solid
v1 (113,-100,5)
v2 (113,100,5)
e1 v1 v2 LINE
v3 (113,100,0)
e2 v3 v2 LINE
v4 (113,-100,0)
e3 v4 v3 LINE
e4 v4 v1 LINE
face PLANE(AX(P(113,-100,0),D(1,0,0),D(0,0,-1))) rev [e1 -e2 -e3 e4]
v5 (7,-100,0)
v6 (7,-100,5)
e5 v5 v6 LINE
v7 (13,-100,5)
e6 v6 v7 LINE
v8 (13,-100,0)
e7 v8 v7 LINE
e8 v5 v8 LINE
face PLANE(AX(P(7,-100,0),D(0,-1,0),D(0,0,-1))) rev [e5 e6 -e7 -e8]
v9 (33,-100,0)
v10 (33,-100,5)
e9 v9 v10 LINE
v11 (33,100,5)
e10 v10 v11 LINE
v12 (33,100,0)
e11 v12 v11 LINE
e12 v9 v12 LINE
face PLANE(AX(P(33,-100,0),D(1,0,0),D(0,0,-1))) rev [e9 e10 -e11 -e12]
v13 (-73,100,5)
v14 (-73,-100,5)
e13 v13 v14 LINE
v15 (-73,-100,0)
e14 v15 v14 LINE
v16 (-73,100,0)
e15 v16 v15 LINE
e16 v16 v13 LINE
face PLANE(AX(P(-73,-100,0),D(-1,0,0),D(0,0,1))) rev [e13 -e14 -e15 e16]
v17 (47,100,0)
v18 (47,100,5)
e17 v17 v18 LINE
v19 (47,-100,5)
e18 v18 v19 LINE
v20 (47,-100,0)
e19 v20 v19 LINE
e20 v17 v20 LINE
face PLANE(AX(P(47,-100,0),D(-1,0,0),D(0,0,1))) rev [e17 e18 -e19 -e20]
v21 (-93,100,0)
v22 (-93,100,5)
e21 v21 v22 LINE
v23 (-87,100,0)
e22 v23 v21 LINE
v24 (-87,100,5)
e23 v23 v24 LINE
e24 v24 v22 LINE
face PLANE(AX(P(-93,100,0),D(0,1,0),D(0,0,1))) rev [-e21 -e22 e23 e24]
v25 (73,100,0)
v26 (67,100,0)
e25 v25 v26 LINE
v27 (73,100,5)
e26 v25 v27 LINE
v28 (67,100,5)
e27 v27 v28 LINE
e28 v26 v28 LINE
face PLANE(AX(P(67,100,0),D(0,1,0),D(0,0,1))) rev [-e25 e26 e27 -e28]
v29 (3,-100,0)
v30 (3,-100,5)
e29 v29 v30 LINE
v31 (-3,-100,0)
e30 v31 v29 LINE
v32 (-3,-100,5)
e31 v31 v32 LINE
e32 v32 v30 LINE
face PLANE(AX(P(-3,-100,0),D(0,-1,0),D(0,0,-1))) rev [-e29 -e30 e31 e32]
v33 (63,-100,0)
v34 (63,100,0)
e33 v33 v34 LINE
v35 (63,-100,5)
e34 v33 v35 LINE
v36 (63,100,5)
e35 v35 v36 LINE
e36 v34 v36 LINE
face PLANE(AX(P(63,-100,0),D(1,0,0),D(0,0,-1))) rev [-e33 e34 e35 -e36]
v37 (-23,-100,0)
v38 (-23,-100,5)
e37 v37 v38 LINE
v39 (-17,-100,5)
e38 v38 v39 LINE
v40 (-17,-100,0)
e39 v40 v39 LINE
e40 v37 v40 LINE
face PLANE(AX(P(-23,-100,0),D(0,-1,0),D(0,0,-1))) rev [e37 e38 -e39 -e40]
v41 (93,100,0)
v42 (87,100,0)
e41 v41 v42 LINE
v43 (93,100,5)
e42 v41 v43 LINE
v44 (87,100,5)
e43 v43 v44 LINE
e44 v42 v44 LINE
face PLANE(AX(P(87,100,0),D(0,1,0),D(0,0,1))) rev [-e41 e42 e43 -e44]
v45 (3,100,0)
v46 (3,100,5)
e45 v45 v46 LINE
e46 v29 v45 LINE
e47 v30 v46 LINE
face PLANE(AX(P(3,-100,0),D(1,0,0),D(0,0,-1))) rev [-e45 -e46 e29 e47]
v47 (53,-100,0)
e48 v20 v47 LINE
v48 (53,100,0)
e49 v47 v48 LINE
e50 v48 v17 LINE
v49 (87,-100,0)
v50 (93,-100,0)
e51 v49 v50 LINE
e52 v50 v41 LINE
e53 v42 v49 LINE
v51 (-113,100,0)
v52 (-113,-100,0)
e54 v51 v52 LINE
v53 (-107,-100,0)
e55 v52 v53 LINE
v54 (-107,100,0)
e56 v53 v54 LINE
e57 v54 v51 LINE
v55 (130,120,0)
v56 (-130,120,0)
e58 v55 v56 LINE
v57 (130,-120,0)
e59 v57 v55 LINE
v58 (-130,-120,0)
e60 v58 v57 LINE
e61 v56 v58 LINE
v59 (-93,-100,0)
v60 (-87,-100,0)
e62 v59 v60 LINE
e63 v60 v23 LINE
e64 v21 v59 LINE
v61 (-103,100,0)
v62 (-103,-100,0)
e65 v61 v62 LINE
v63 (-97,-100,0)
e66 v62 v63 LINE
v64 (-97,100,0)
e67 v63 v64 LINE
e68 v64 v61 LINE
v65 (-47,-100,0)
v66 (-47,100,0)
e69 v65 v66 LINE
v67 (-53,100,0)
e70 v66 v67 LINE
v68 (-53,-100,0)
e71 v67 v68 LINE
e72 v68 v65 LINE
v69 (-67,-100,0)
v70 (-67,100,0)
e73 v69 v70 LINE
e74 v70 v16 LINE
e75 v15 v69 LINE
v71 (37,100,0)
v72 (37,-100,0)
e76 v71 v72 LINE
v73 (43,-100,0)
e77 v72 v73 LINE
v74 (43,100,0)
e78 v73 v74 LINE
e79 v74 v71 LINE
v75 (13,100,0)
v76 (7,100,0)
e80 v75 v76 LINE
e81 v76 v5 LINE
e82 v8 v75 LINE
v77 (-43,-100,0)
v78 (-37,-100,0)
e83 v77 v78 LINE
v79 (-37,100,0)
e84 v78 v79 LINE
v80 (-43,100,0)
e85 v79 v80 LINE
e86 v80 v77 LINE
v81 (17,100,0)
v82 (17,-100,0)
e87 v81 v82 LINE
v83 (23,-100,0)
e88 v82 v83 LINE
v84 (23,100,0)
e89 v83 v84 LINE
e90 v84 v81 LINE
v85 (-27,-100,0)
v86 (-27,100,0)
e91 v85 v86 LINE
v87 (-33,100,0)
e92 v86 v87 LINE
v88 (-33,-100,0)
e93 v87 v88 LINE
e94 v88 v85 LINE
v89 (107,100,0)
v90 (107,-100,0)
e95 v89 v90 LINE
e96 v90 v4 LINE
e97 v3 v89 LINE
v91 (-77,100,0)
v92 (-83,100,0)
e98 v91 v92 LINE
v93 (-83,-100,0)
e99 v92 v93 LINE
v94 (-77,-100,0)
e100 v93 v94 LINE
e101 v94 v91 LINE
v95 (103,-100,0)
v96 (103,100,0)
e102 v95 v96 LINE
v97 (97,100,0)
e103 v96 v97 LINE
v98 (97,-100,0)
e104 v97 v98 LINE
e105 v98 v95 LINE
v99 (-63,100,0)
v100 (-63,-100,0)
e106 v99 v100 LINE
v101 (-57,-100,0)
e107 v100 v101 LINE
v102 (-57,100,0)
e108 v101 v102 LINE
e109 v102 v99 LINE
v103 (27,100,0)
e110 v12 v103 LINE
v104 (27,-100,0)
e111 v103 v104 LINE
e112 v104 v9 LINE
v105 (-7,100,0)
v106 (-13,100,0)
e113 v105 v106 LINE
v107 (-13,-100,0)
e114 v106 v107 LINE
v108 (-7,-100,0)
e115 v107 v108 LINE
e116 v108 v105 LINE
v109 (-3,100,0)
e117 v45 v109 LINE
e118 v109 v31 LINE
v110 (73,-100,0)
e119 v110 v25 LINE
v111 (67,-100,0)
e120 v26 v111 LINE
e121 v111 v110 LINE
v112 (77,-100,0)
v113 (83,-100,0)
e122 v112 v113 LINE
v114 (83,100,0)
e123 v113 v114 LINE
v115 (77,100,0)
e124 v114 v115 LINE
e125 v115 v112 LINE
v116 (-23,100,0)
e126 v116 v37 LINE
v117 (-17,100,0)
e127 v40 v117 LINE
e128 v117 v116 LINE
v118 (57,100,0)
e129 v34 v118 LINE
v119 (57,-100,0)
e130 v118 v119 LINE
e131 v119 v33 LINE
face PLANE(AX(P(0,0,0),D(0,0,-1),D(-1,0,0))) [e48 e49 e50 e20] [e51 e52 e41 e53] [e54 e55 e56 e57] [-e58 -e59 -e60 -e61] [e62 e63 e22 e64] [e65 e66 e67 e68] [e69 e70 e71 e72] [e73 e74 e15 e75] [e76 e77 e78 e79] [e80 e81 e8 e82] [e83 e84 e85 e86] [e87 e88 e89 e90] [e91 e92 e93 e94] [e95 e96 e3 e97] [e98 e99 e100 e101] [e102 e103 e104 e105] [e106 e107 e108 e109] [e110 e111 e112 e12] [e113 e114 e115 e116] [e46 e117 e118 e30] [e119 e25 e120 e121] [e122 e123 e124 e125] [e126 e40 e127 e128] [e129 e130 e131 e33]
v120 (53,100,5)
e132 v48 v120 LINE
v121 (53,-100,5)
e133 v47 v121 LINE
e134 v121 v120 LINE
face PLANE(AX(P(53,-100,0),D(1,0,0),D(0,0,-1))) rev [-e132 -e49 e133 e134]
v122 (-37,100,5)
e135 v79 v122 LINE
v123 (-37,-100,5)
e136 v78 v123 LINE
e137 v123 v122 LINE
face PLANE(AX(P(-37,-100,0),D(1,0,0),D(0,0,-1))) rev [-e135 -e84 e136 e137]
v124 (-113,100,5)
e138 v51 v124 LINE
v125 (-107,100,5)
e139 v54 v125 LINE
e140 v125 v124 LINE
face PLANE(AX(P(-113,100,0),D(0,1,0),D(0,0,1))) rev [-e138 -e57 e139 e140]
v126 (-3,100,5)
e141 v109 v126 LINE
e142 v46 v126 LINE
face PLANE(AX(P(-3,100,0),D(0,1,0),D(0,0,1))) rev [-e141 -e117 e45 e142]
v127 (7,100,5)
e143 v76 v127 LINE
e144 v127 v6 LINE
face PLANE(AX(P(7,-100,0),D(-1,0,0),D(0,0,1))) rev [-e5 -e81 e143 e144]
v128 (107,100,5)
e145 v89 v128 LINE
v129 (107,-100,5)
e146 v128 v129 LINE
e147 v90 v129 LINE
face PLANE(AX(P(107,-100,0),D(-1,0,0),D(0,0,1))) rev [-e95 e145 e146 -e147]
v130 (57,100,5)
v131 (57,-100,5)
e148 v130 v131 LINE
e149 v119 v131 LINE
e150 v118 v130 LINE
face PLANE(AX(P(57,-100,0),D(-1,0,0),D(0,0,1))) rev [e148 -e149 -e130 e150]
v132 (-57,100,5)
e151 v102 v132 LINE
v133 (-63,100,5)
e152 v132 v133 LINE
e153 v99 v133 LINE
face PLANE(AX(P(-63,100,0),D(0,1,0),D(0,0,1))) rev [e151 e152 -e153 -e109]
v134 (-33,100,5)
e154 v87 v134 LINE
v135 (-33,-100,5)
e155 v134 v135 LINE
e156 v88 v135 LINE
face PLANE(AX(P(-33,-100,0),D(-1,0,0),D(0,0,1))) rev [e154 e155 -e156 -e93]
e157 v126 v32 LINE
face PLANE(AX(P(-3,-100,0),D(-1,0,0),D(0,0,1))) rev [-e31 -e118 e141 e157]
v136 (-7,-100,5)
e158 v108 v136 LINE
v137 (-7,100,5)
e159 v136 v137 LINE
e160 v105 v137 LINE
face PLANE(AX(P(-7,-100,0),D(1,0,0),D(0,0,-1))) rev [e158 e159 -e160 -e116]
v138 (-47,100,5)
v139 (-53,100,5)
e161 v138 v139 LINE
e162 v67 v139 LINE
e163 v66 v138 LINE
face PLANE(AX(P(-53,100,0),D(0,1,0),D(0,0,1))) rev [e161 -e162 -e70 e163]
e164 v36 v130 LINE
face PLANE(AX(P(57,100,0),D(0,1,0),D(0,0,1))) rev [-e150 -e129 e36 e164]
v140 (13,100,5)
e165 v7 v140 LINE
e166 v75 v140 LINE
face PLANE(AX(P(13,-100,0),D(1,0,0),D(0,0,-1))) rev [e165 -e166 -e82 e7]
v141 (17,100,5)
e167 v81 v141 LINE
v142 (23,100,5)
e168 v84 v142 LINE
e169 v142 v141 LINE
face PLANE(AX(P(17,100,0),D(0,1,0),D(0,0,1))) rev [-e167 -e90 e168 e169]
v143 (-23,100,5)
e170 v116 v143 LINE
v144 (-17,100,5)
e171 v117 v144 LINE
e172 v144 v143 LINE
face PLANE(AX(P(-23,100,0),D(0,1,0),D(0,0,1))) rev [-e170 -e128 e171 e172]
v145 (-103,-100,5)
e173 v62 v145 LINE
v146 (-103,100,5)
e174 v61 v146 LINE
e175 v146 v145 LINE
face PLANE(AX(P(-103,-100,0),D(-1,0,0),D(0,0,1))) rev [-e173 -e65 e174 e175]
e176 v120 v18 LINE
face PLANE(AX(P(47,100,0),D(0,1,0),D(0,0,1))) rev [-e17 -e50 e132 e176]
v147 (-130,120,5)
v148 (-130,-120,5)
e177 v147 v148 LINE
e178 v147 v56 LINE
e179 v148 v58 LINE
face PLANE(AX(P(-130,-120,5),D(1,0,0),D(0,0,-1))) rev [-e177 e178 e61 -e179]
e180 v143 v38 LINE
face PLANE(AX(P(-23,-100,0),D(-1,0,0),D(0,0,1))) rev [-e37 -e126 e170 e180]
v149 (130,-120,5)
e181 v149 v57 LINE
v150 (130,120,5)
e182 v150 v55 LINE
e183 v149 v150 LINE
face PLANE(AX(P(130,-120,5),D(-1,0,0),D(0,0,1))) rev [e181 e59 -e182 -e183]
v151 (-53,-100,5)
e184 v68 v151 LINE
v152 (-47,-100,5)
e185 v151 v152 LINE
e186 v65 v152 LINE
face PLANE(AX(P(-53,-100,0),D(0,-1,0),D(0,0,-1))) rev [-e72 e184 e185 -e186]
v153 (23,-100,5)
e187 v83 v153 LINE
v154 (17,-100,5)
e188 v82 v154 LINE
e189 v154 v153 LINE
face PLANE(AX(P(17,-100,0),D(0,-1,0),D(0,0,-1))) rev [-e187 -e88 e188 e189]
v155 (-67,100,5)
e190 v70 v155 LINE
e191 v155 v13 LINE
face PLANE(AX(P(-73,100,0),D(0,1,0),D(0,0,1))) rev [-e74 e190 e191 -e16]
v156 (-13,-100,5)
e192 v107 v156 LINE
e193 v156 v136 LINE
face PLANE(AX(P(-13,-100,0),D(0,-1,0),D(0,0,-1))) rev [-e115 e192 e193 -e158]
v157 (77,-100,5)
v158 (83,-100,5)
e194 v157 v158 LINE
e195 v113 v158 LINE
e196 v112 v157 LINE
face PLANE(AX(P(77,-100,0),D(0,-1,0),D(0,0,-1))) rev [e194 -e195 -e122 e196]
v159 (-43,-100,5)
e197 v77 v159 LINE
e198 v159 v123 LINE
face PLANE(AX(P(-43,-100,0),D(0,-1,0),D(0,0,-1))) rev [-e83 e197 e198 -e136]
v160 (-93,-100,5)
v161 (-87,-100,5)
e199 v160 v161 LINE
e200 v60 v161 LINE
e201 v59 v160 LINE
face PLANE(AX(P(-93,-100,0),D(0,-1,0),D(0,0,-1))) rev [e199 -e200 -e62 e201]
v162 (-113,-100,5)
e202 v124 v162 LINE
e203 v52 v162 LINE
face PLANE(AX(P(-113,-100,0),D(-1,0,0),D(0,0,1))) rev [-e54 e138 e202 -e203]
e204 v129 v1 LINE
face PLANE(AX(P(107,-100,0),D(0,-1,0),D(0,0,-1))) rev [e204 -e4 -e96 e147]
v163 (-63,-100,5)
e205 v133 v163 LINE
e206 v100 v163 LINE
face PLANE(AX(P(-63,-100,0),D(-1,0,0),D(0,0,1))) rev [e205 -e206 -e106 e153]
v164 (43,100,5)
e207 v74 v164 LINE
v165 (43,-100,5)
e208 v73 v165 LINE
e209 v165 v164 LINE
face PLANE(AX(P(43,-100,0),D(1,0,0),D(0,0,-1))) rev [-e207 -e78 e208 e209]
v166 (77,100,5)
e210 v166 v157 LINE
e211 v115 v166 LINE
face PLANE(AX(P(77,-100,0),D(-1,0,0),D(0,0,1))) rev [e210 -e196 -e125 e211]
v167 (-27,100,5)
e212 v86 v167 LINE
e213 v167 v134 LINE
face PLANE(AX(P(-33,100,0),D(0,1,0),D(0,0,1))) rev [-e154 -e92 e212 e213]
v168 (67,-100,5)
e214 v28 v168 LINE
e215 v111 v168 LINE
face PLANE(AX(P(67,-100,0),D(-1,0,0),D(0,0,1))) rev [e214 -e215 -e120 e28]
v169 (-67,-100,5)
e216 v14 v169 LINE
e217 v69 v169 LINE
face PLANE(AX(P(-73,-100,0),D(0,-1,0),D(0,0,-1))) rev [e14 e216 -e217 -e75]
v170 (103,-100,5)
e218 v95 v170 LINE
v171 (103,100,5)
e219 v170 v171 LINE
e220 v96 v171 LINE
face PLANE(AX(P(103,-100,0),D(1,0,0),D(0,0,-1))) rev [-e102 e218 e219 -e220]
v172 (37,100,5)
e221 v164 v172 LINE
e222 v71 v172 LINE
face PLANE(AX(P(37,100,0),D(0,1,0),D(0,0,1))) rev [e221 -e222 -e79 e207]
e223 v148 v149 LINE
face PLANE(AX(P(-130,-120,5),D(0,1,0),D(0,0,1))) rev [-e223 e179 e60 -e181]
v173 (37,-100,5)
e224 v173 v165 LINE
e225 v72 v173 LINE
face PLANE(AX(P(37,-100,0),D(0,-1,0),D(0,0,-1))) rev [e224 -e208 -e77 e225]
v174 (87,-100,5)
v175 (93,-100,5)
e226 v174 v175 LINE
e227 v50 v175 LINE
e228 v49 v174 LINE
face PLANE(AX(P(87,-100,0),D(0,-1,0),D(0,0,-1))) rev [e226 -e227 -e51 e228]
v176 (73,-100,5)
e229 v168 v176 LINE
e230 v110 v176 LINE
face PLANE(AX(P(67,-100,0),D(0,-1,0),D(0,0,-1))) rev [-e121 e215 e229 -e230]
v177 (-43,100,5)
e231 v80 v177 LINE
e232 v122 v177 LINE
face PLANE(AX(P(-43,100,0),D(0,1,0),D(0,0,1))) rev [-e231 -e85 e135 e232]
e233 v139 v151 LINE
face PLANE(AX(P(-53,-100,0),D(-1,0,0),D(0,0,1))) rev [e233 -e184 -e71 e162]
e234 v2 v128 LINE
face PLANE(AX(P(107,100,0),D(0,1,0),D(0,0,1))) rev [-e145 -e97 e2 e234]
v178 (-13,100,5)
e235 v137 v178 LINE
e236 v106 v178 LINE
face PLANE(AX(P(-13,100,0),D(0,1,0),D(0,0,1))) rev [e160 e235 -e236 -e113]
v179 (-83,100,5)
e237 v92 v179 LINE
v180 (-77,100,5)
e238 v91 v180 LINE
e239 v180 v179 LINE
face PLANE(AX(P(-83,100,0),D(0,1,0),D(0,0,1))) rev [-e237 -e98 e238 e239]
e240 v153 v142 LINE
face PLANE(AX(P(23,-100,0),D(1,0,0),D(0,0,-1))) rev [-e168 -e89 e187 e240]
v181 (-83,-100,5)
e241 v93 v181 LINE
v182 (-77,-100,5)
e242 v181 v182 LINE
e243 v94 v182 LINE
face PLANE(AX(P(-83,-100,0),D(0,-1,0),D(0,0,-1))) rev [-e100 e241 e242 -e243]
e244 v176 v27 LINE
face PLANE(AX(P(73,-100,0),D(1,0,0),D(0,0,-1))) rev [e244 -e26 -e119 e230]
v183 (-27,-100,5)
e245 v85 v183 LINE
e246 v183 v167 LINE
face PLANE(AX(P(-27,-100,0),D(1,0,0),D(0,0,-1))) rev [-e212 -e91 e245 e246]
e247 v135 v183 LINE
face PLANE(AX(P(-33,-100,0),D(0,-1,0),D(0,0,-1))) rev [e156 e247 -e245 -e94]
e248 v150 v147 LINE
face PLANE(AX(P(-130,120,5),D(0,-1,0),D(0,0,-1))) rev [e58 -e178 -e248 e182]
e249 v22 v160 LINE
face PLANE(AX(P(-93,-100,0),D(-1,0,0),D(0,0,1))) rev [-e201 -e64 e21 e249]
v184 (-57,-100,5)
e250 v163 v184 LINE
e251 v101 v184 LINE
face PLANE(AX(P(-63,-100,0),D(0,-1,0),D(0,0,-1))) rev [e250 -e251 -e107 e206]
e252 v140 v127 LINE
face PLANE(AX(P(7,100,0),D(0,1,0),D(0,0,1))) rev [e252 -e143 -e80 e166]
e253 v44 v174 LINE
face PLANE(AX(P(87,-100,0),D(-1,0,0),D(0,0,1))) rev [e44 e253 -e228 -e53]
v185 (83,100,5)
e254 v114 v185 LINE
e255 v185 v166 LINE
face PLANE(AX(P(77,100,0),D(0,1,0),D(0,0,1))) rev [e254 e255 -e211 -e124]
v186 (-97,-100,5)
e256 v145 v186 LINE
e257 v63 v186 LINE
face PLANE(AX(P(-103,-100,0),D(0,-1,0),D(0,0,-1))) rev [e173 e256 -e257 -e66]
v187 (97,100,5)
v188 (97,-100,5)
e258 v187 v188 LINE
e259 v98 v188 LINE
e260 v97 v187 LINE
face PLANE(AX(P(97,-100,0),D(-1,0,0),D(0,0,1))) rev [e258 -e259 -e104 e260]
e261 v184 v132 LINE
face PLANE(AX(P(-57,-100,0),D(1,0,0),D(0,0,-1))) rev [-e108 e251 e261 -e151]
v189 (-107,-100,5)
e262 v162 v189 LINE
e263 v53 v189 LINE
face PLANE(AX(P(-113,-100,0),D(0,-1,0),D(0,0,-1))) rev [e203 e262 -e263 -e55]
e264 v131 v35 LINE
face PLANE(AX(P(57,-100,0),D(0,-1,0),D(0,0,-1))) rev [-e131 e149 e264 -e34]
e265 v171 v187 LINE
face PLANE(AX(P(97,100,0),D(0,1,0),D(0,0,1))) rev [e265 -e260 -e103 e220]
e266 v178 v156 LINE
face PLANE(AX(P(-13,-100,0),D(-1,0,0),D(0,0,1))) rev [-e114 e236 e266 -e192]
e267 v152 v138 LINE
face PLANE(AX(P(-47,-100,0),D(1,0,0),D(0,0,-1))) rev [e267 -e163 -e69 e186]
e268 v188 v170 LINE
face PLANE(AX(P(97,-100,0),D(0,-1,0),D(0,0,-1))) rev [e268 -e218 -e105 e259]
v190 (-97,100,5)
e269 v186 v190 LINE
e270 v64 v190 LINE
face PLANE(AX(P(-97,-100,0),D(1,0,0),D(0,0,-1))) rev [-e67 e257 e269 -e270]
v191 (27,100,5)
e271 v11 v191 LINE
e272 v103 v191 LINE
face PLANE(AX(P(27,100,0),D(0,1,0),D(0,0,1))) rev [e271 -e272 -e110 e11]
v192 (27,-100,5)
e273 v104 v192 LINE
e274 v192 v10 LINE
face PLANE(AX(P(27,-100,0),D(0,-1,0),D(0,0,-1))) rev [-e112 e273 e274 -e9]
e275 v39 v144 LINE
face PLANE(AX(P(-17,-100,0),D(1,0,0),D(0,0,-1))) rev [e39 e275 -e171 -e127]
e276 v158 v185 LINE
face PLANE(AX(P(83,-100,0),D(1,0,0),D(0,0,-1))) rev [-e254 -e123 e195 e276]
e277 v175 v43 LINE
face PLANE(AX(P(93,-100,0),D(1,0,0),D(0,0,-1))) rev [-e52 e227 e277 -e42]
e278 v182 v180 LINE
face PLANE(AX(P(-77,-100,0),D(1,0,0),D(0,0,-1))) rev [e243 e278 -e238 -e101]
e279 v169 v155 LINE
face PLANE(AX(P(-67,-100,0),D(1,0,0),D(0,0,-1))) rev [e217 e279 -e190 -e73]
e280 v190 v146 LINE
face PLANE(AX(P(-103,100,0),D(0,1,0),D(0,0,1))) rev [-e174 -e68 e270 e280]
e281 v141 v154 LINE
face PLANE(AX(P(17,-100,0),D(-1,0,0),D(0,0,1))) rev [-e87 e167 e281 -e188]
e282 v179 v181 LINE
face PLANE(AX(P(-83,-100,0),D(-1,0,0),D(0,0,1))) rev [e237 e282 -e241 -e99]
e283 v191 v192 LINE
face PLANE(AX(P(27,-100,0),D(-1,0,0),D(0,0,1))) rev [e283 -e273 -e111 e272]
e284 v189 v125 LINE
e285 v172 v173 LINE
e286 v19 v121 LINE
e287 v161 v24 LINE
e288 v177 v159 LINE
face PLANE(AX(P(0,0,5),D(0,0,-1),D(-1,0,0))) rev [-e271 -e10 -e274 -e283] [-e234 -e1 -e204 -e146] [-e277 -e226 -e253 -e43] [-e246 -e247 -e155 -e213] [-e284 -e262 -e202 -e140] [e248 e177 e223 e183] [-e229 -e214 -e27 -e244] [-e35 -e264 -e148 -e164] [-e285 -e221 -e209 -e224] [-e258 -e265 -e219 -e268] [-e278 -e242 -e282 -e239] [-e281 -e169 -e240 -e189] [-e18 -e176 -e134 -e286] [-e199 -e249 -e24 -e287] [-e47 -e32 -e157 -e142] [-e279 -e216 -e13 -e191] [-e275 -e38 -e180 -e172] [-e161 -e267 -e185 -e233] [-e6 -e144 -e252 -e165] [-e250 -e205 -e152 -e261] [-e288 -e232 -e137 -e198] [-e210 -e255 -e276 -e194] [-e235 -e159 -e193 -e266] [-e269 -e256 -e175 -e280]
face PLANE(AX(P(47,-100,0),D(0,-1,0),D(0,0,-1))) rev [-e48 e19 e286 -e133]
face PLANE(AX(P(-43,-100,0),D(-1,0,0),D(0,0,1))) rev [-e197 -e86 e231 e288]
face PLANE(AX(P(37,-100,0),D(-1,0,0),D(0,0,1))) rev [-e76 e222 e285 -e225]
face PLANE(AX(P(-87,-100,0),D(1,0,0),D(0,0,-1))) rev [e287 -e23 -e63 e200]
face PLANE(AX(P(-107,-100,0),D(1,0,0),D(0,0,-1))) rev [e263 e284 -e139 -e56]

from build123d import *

# Parameters (mm, degrees)
SKETCH_1_W                 = 260
SKETCH_1_H                 = 240
EXTRUDE_1_DEPTH            = 5
SKETCH_2_W                 = 6
SKETCH_2_H                 = 200
CUT_EXTRUDE_1_DEPTH        = 177.988700204
PATTERN_LINEAR_1_COUNT     = 12
PATTERN_LINEAR_1_PITCH     = 10
PATTERN_LINEAR_1_COL_COUNT = 12
PATTERN_LINEAR_1_COL_PITCH = 10


with BuildPart() as part:
    # 草图1 → 凸台-拉伸1 (new body)
    with BuildSketch(Plane.XY):
        Rectangle(SKETCH_1_W, SKETCH_1_H)
    extrude(amount=EXTRUDE_1_DEPTH)

    # 草图2 → 切除-拉伸1 (cut, through all)
    with BuildSketch(Plane.XY.offset(5)):
        Rectangle(SKETCH_2_W, SKETCH_2_H)
    cut_extrude_1 = extrude(amount=-CUT_EXTRUDE_1_DEPTH, mode=Mode.SUBTRACT)

    # 阵列(线性)1: 切除-拉伸1 ×12
    with Locations(*[(i * PATTERN_LINEAR_1_PITCH, 0, 0) for i in range(1, PATTERN_LINEAR_1_COUNT)]):
        add(cut_extrude_1, mode=Mode.SUBTRACT)

    # 阵列(线性)1 col: 切除-拉伸1 ×12
    with Locations(*[(-i * PATTERN_LINEAR_1_COL_PITCH, 0, 0) for i in range(1, PATTERN_LINEAR_1_COL_COUNT)]):
        add(cut_extrude_1, mode=Mode.SUBTRACT)


solid = part.part
